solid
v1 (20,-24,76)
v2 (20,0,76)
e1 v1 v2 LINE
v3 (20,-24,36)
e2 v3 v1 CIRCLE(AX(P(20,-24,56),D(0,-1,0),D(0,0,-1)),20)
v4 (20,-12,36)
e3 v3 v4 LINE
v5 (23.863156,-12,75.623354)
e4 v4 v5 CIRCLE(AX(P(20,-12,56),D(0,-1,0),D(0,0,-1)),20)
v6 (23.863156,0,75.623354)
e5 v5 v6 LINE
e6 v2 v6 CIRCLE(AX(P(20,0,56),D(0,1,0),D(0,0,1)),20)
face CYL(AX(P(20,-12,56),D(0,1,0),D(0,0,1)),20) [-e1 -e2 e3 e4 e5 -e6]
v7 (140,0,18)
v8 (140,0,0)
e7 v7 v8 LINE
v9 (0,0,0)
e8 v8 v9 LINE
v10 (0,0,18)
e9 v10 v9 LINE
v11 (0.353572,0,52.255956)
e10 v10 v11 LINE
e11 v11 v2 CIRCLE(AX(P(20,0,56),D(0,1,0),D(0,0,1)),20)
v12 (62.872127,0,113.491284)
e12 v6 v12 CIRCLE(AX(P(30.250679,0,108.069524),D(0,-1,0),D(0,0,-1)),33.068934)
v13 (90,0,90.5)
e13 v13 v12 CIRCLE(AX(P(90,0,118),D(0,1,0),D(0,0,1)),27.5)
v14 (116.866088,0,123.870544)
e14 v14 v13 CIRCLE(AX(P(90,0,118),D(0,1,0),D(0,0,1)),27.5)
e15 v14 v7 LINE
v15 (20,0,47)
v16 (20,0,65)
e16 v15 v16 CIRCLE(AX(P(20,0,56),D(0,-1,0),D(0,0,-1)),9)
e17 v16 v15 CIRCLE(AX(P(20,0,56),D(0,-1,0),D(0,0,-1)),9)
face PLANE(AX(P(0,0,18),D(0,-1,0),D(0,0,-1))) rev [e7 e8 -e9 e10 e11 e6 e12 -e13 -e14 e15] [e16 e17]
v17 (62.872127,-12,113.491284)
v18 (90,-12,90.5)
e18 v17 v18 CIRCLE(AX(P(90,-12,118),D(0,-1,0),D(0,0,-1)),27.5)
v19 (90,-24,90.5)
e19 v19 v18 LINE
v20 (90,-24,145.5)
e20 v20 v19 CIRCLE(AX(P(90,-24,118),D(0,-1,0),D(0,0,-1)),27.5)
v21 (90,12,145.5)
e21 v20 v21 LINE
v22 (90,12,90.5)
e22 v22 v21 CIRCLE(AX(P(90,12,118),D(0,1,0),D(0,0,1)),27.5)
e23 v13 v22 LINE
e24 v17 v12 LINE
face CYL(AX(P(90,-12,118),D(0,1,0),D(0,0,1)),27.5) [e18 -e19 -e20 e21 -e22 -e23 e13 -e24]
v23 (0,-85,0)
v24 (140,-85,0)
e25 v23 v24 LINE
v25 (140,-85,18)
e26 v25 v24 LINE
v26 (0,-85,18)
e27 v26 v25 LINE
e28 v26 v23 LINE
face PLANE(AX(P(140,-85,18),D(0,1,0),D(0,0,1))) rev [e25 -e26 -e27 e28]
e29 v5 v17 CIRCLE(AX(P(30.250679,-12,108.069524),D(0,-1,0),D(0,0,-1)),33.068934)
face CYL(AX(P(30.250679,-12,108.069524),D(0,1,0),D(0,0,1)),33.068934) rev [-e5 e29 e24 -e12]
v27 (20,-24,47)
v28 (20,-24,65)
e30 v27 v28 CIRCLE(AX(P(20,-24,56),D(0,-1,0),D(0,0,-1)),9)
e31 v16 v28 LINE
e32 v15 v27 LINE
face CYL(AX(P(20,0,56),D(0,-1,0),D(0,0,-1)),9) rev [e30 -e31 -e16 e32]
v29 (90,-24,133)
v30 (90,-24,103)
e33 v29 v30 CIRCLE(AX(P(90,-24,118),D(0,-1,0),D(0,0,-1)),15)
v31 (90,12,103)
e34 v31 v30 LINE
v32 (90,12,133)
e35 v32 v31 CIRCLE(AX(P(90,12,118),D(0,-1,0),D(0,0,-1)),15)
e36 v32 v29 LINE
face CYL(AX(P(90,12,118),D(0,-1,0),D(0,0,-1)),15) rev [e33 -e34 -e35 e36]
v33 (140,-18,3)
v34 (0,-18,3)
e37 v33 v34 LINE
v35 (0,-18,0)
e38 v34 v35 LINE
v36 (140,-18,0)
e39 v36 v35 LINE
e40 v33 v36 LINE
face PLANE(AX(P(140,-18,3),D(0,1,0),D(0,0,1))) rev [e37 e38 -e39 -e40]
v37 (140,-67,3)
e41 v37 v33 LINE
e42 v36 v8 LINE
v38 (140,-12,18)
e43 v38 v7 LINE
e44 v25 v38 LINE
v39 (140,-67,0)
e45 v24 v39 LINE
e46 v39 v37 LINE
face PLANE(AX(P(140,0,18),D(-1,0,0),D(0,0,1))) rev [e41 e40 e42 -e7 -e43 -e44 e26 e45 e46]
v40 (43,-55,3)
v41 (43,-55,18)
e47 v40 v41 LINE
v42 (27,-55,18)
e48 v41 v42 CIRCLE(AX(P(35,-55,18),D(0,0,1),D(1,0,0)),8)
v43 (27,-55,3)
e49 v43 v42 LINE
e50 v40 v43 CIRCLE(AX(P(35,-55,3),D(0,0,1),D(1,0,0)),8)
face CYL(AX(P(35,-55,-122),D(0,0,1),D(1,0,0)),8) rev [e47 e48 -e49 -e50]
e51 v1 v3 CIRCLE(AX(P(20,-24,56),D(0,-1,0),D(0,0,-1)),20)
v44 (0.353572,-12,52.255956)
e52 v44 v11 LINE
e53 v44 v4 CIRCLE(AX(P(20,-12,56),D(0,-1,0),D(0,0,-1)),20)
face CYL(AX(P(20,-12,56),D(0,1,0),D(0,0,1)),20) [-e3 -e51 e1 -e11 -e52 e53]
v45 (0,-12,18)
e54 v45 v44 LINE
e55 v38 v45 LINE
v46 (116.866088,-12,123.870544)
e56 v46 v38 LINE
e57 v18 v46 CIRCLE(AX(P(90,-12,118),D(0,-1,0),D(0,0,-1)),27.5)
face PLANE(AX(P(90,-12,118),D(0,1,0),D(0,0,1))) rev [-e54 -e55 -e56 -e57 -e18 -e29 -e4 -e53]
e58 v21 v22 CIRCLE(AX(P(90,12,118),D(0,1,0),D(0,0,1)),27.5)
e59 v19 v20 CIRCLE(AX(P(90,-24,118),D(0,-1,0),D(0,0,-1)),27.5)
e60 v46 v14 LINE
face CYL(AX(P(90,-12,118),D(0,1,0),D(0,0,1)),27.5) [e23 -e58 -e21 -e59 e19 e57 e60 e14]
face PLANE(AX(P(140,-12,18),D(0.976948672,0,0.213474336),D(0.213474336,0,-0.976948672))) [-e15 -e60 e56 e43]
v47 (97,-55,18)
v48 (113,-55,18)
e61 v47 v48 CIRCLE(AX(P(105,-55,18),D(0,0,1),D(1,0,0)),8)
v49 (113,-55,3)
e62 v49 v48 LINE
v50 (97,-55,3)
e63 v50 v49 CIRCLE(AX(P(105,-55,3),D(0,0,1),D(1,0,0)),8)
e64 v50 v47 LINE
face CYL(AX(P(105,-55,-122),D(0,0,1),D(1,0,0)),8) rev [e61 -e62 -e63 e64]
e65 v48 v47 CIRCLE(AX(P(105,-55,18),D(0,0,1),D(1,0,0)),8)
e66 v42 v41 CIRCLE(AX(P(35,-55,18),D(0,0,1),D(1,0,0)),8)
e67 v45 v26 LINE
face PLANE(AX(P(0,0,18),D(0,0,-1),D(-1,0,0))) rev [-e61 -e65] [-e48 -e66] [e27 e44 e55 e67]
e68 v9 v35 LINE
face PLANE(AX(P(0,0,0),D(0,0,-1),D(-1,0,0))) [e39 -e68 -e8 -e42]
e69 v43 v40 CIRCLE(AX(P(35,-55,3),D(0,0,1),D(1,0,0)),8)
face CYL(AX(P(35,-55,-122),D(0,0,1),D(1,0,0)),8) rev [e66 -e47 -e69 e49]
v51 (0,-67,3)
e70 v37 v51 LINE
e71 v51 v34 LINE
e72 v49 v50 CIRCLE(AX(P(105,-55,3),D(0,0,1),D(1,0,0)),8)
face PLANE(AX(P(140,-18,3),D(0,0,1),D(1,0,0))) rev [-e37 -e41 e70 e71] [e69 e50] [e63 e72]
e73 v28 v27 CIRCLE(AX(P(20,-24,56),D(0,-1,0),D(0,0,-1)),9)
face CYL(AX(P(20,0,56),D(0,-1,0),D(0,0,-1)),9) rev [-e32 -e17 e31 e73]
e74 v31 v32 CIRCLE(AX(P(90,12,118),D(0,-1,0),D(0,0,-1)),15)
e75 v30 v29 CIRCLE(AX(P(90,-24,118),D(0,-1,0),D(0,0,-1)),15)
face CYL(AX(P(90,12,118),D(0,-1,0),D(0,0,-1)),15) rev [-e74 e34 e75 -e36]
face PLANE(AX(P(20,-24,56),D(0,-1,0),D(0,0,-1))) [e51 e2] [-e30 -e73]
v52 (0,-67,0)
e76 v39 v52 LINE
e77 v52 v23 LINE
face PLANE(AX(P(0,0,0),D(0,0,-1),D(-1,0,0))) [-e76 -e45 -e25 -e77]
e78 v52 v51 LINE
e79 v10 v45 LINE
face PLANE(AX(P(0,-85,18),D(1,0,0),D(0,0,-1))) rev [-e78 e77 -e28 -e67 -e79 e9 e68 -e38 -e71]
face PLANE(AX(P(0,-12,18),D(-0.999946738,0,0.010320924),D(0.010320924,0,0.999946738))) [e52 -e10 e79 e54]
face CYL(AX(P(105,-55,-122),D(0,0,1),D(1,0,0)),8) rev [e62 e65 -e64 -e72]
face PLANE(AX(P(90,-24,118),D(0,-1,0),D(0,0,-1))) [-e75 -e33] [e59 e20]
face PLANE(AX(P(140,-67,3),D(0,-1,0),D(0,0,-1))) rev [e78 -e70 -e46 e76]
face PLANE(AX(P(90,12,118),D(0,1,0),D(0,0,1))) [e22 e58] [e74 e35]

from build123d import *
from build123d.topology import SkipClean

# Parameters (mm, degrees)
BASE_PLATE_SKETCH_W             = 140
BASE_PLATE_SKETCH_H             = 85
BASE_PLATE_18MM_DEPTH           = 18
PLATE_PROFILE_CUT_SKETCH_W      = 3
PLATE_PROFILE_CUT_SKETCH_H      = 49
PLATE_PROFILE_CUT_DEPTH         = 140
NOTCH_16X16_SKETCH_R            = 8
NOTCH_16X16_DEPTH               = 140
SMALL_EYE_BOSS_40_SKETCH_R      = 20
SMALL_EYE_BOSS_40_DEPTH         = 12
LARGE_EYE_BOSS_55_SKETCH_R      = 27.5
LARGE_EYE_BOSS_55_DEPTH         = 12
EYE_LINK_WEB_DEPTH              = 12
LARGE_START                     = 12
LARGE_EYE_CAP_55_SKETCH_R       = 27.5
LARGE_EYE_CAP_55_DEPTH          = 12
LARGE_EYE_EXTENSION_55_SKETCH_R = 27.5
LARGE_EYE_EXTENSION_55_DEPTH    = 12
SMALL_EYE_EXTENSION_40_SKETCH_R = 20
SMALL_EYE_EXTENSION_40_DEPTH    = 12
LARGE_EYE_BORE_30_SKETCH_R      = 15
LARGE_EYE_BORE_30_DEPTH         = 36
SMALL_EYE_BORE_18_SKETCH_R      = 9
SMALL_EYE_BORE_18_DEPTH         = 24


with BuildPart() as part:
    # Base Plate Sketch → Base Plate 18mm (new body)
    with BuildSketch(Plane.XY):
        with Locations((70, -42.5)):
            Rectangle(BASE_PLATE_SKETCH_W, BASE_PLATE_SKETCH_H)
    extrude(amount=BASE_PLATE_18MM_DEPTH)

    # Plate Profile Cut Sketch → Plate Profile Cut (cut)
    with BuildSketch(Plane.ZY):
        with Locations((1.5, -42.5)):
            Rectangle(PLATE_PROFILE_CUT_SKETCH_W, PLATE_PROFILE_CUT_SKETCH_H)
    extrude(amount=-PLATE_PROFILE_CUT_DEPTH, mode=Mode.SUBTRACT)

    # Notch 16x16 Sketch → Notch 16x16 (cut)
    with BuildSketch(Plane.XY.offset(18)):
        with Locations((35, -55)):
            Circle(NOTCH_16X16_SKETCH_R)
        with Locations((105, -55)):
            Circle(NOTCH_16X16_SKETCH_R)
    extrude(amount=-NOTCH_16X16_DEPTH, mode=Mode.SUBTRACT)



with BuildPart() as body_2:
    # Small Eye Boss Ø40 Sketch → Small Eye Boss Ø40 (new body)
    with BuildSketch(Plane(origin=(0, 0, 0), x_dir=(1, 0, 0), z_dir=(0, 1, 0))):
        with Locations(Location((20, -56, 0), (0, 0, 270))):
            Circle(SMALL_EYE_BOSS_40_SKETCH_R)
    extrude(amount=-SMALL_EYE_BOSS_40_DEPTH)


with BuildPart() as body_3:
    # Large Eye Boss Ø55 Sketch → Large Eye Boss Ø55 (new body)
    with BuildSketch(Plane(origin=(0, 0, 0), x_dir=(1, 0, 0), z_dir=(0, 1, 0))):
        with Locations(Location((90, -118, 0), (0, 0, 270))):
            Circle(LARGE_EYE_BOSS_55_SKETCH_R)
    extrude(amount=-LARGE_EYE_BOSS_55_DEPTH)


with BuildPart() as part_1:
    add(part.part)

    add(body_2.part)  # Eye Link Web merges body 2

    add(body_3.part)  # Eye Link Web merges body 3
    # Eye Link Web Sketch → Eye Link Web (add)
    with BuildSketch(Plane(origin=(0, 0, 0), x_dir=(1, 0, 0), z_dir=(0, 1, 0))):
        with BuildLine():
            Line((0, -18), (0.353571949, -52.255956083))
            ThreePointArc((0.353571949, -52.255956083), (34.099175171, -41.815034032), (23.863156104, -75.623354069))
            ThreePointArc((23.863156104, -75.623354069), (53.284344418, -84.341805302), (62.872127171, -113.491284467))
            ThreePointArc((62.872127171, -113.491284467), (95.191280297, -90.994433743), (116.866088482, -123.870544241))
            Line((116.866088482, -123.870544241), (140, -18))
            Line((140, -18), (0, -18))
        make_face()
    extrude(amount=-EYE_LINK_WEB_DEPTH)

    # Large Eye Cap Ø55 Sketch → Large Eye Cap Ø55 (add)
    with BuildSketch(Plane(origin=(0, 0, 0), x_dir=(1, 0, 0), z_dir=(0, 1, 0)).offset(LARGE_START)):
        with Locations(Location((90, -118, 0), (0, 0, 270))):
            Circle(LARGE_EYE_CAP_55_SKETCH_R)
    extrude(amount=-LARGE_EYE_CAP_55_DEPTH)

    # Large Eye Extension Ø55 Sketch → Large Eye Extension Ø55 (add)
    with SkipClean():  # the faces are left unmerged after this step: merging them gives an invalid solid
        with BuildSketch(Plane.XZ.offset(12)):
            with Locations(Location((90, 118, 0), (0, 0, 90))):
                Circle(LARGE_EYE_EXTENSION_55_SKETCH_R)
        extrude(amount=LARGE_EYE_EXTENSION_55_DEPTH)

    # Small Eye Extension Ø40 Sketch → Small Eye Extension Ø40 (add)
    with SkipClean():  # the faces are left unmerged after this step: merging them gives an invalid solid
        with BuildSketch(Plane.XZ.offset(12)):
            with Locations(Location((20, 56, 0), (0, 0, 78.862872248))):
                Circle(SMALL_EYE_EXTENSION_40_SKETCH_R)
        extrude(amount=SMALL_EYE_EXTENSION_40_DEPTH)

    # Large Eye Bore Ø30 Sketch → Large Eye Bore Ø30 (cut)
    with SkipClean():  # the faces are left unmerged after this step: merging them gives an invalid solid
        with BuildSketch(Plane.XZ.offset(24)):
            with Locations(Location((90, 118, 0), (0, 0, 270))):
                Circle(LARGE_EYE_BORE_30_SKETCH_R)
        extrude(amount=-LARGE_EYE_BORE_30_DEPTH, mode=Mode.SUBTRACT)

    # Small Eye Bore Ø18 Sketch → Small Eye Bore Ø18 (cut)
    with SkipClean():  # the faces are left unmerged after this step: merging them gives an invalid solid
        with BuildSketch(Plane.XZ.offset(24)):
            with Locations(Location((20, 56, 0), (0, 0, 270))):
                Circle(SMALL_EYE_BORE_18_SKETCH_R)
        extrude(amount=-SMALL_EYE_BORE_18_DEPTH, mode=Mode.SUBTRACT)


solid = part_1.part
